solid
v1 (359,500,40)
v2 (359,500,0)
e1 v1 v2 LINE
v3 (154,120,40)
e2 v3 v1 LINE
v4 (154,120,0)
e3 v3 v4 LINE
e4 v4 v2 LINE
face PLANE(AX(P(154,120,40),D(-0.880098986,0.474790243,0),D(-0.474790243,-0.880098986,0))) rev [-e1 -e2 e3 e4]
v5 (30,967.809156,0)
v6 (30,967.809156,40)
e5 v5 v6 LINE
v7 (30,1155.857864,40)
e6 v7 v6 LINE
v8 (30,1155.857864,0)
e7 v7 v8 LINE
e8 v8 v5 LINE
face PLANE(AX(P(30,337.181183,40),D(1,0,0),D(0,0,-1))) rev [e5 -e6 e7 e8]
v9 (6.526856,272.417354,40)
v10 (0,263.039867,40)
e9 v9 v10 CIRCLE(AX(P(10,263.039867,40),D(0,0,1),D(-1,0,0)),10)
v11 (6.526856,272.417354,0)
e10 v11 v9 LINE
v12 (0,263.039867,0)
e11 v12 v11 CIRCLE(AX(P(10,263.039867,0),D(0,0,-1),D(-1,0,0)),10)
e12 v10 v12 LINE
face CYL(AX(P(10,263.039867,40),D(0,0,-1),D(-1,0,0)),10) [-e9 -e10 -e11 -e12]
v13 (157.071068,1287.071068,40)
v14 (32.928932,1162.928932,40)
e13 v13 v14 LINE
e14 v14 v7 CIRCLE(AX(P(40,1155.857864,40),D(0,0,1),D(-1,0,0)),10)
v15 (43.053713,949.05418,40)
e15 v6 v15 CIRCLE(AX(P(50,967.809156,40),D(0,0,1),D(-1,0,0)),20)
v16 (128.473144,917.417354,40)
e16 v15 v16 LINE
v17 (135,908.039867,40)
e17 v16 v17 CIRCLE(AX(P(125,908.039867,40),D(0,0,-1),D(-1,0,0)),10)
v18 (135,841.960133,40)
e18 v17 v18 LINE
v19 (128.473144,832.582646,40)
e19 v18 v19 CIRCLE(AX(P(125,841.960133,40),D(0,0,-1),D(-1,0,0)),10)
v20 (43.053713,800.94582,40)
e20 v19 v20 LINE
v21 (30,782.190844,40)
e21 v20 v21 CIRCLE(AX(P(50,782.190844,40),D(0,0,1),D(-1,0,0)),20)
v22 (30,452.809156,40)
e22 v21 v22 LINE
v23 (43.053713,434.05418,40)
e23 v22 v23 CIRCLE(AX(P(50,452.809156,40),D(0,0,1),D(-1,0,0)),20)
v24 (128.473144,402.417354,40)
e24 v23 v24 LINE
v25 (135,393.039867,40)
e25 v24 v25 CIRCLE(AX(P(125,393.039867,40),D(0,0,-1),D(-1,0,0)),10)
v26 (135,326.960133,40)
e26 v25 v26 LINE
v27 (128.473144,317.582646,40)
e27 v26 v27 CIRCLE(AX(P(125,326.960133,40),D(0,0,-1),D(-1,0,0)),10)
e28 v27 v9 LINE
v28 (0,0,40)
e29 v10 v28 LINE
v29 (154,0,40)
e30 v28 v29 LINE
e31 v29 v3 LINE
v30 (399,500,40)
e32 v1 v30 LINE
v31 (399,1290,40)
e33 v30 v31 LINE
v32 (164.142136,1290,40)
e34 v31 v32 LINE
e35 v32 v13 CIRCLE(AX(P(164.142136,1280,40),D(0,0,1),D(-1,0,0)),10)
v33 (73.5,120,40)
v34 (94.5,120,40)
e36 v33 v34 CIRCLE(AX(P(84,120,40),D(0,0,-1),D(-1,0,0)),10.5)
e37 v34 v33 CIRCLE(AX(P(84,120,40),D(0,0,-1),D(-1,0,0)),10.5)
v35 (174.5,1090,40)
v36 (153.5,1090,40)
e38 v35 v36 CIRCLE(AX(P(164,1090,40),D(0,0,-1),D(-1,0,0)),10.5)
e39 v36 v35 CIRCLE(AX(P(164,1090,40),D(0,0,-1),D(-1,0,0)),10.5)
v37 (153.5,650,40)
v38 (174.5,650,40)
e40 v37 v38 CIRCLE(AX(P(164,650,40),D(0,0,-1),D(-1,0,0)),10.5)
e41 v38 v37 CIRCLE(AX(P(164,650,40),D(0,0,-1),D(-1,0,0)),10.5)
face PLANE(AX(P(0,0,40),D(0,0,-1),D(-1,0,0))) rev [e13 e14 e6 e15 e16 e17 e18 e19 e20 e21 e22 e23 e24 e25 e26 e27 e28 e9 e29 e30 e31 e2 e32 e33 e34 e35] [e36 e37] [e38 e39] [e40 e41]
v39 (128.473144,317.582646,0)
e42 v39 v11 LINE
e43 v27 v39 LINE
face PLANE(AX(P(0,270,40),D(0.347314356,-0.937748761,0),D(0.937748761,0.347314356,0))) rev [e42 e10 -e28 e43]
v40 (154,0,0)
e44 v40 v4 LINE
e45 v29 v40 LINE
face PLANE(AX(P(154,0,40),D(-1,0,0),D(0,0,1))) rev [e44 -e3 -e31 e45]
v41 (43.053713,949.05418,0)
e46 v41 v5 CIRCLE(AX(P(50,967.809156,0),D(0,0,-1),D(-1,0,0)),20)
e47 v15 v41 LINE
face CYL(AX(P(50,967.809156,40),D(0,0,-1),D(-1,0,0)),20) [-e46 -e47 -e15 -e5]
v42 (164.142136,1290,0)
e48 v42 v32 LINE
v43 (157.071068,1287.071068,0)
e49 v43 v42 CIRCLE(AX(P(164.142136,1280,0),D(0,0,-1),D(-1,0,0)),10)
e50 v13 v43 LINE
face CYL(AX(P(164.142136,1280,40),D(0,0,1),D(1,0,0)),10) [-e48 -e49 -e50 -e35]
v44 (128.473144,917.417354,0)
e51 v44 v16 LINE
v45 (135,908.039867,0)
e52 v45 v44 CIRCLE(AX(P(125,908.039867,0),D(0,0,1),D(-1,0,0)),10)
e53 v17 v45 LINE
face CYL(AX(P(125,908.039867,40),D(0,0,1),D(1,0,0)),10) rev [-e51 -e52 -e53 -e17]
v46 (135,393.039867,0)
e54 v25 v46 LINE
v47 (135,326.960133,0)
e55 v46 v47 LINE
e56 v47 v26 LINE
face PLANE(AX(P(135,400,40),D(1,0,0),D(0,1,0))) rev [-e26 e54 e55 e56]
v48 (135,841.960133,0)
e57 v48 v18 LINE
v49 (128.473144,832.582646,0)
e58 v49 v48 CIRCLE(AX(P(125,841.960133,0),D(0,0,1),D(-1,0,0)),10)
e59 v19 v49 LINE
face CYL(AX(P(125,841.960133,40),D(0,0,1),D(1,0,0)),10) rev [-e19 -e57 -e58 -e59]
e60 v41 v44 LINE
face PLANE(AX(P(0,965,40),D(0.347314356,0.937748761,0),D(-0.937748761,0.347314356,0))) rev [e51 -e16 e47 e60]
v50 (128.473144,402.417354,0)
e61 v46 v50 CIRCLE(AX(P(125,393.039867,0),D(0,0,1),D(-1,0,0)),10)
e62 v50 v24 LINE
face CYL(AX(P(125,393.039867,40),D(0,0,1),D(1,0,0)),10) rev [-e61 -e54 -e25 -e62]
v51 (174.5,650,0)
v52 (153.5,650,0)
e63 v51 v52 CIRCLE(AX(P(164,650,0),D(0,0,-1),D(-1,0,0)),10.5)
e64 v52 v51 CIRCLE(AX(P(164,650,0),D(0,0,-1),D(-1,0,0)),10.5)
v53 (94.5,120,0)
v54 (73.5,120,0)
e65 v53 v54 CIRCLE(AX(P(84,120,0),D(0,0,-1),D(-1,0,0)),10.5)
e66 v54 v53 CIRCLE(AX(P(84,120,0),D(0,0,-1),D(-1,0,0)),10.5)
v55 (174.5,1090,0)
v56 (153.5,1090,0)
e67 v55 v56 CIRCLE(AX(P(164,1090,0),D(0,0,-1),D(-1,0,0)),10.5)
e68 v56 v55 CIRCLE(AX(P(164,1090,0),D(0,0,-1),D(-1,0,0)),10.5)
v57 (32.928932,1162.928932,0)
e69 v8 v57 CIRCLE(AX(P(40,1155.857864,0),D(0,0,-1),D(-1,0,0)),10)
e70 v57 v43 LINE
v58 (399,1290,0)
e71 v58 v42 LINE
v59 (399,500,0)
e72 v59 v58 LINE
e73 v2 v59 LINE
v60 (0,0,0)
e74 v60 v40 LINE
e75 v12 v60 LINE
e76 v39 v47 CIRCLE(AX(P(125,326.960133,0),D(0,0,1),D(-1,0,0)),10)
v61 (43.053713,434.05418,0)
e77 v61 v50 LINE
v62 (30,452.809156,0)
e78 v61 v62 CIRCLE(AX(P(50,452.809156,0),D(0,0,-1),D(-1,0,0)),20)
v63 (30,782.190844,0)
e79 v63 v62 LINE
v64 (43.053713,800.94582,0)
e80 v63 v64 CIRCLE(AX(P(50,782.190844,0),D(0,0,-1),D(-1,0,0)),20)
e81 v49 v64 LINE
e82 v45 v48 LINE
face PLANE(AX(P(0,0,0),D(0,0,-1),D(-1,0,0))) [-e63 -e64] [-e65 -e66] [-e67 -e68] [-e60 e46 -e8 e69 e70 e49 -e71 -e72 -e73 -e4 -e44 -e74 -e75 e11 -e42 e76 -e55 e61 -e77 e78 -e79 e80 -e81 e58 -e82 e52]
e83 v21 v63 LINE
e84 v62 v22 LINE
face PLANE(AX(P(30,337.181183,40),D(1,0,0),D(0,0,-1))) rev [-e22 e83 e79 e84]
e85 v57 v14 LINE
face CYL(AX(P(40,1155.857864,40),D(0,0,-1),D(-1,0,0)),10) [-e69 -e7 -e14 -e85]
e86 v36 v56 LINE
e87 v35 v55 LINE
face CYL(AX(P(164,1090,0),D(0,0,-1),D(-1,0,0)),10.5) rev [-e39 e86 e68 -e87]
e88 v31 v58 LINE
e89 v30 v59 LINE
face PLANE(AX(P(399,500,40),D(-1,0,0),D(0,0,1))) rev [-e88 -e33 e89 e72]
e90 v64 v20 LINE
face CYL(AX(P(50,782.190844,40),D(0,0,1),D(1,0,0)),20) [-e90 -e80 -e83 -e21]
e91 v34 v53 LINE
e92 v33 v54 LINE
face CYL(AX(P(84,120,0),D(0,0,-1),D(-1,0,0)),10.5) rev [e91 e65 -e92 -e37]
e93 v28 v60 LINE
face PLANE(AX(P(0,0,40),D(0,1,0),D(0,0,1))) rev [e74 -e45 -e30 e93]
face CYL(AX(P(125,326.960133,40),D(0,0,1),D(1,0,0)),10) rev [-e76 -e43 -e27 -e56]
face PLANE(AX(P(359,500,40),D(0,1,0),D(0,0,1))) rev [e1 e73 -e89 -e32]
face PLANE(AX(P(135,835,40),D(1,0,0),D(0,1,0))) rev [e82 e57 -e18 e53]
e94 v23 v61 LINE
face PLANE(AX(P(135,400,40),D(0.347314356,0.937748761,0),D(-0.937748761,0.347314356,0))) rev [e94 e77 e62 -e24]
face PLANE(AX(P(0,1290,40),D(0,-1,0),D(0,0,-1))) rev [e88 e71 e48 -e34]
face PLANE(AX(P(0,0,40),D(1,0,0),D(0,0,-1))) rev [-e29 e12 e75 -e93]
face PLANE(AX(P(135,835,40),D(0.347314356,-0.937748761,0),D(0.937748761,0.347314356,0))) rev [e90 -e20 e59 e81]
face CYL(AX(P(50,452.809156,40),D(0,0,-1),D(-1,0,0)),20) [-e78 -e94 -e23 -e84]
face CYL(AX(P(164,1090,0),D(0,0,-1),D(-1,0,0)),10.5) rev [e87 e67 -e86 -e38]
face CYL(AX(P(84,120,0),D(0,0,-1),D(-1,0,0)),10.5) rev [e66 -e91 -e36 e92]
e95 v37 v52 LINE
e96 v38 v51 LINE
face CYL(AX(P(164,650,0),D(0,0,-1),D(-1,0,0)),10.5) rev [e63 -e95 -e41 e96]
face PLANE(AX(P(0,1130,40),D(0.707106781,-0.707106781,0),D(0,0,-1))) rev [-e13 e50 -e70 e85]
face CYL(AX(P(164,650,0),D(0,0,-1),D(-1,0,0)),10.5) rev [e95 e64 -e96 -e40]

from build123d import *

# Parameters (mm, degrees)
BOSS_EXTRUDE1_DEPTH = 40
CHAMFER1_SIZE       = 160
M24_TAPPED_HOLE1_D  = 21
CUT_EXTRUDE1_DEPTH  = 1351.88896657
FILLET1_R           = 10
SKETCH4_W           = 30
SKETCH4_H           = 822.818816594
CUT_EXTRUDE2_DEPTH  = 1351.88896657
FILLET2_R           = 20
FILLET3_R           = 10


with BuildPart() as part:
    # Sketch1 → Boss-Extrude1 (new body)
    with BuildSketch(Plane.XY):
        Polygon((154, 0), (154, 120), (359, 500), (399, 500), (399, 1290), (0, 1290), (0, 0), align=None)
    extrude(amount=BOSS_EXTRUDE1_DEPTH)

    # Chamfer1
    chamfer1_edges = [part.edges().sort_by_distance(p)[0] for p in [
        (0, 1290, 20),
    ]]
    chamfer(chamfer1_edges, length=CHAMFER1_SIZE)

    # M24 Tapped Hole1 (through all)
    with Locations(Plane(origin=(164, 1090, 0), x_dir=(-1, 0, 0), z_dir=(0, 0, -1))):
        with Locations((0, 0), (0, -440), (80, -970)):
            Hole(M24_TAPPED_HOLE1_D / 2)

    # Sketch3 → Cut-Extrude1 (cut, through all)
    with BuildSketch(Plane(origin=(0, 0, 0), x_dir=(-1, 0, 0), z_dir=(0, 0, -1))):
        Polygon((-135, 835), (0, 785), (0, 965), (-135, 915), align=None)
        Polygon((-135, 400), (-135, 320), (0, 270), (0, 450), align=None)
    extrude(amount=-CUT_EXTRUDE1_DEPTH, mode=Mode.SUBTRACT)

    # Fillet1
    fillet1_edges = [part.edges().sort_by_distance(p)[0] for p in [
        (135, 400, 20),
        (0, 450, 20),
        (0, 270, 20),
        (135, 320, 20),
        (0, 965, 20),
        (0, 785, 20),
        (135, 835, 20),
        (135, 915, 20),
    ]]
    fillet(fillet1_edges, radius=FILLET1_R)

    # Sketch4 → Cut-Extrude2 (cut, through all)
    with BuildSketch(Plane(origin=(0, 0, 0), x_dir=(-1, 0, 0), z_dir=(0, 0, -1))):
        with Locations((-15, 748.590591703)):
            Rectangle(SKETCH4_W, SKETCH4_H)
    extrude(amount=-CUT_EXTRUDE2_DEPTH, mode=Mode.SUBTRACT)

    # Fillet2
    fillet2_edges = [part.edges().sort_by_distance(p)[0] for p in [
        (30, 953.888888889, 20),
        (30, 438.888888889, 20),
        (30, 796.111111111, 20),
    ]]
    fillet(fillet2_edges, radius=FILLET2_R)

    # Fillet3
    fillet3_edges = [part.edges().sort_by_distance(p)[0] for p in [
        (30, 1160, 20),
        (160, 1290, 20),
    ]]
    fillet(fillet3_edges, radius=FILLET3_R)


solid = part.part
